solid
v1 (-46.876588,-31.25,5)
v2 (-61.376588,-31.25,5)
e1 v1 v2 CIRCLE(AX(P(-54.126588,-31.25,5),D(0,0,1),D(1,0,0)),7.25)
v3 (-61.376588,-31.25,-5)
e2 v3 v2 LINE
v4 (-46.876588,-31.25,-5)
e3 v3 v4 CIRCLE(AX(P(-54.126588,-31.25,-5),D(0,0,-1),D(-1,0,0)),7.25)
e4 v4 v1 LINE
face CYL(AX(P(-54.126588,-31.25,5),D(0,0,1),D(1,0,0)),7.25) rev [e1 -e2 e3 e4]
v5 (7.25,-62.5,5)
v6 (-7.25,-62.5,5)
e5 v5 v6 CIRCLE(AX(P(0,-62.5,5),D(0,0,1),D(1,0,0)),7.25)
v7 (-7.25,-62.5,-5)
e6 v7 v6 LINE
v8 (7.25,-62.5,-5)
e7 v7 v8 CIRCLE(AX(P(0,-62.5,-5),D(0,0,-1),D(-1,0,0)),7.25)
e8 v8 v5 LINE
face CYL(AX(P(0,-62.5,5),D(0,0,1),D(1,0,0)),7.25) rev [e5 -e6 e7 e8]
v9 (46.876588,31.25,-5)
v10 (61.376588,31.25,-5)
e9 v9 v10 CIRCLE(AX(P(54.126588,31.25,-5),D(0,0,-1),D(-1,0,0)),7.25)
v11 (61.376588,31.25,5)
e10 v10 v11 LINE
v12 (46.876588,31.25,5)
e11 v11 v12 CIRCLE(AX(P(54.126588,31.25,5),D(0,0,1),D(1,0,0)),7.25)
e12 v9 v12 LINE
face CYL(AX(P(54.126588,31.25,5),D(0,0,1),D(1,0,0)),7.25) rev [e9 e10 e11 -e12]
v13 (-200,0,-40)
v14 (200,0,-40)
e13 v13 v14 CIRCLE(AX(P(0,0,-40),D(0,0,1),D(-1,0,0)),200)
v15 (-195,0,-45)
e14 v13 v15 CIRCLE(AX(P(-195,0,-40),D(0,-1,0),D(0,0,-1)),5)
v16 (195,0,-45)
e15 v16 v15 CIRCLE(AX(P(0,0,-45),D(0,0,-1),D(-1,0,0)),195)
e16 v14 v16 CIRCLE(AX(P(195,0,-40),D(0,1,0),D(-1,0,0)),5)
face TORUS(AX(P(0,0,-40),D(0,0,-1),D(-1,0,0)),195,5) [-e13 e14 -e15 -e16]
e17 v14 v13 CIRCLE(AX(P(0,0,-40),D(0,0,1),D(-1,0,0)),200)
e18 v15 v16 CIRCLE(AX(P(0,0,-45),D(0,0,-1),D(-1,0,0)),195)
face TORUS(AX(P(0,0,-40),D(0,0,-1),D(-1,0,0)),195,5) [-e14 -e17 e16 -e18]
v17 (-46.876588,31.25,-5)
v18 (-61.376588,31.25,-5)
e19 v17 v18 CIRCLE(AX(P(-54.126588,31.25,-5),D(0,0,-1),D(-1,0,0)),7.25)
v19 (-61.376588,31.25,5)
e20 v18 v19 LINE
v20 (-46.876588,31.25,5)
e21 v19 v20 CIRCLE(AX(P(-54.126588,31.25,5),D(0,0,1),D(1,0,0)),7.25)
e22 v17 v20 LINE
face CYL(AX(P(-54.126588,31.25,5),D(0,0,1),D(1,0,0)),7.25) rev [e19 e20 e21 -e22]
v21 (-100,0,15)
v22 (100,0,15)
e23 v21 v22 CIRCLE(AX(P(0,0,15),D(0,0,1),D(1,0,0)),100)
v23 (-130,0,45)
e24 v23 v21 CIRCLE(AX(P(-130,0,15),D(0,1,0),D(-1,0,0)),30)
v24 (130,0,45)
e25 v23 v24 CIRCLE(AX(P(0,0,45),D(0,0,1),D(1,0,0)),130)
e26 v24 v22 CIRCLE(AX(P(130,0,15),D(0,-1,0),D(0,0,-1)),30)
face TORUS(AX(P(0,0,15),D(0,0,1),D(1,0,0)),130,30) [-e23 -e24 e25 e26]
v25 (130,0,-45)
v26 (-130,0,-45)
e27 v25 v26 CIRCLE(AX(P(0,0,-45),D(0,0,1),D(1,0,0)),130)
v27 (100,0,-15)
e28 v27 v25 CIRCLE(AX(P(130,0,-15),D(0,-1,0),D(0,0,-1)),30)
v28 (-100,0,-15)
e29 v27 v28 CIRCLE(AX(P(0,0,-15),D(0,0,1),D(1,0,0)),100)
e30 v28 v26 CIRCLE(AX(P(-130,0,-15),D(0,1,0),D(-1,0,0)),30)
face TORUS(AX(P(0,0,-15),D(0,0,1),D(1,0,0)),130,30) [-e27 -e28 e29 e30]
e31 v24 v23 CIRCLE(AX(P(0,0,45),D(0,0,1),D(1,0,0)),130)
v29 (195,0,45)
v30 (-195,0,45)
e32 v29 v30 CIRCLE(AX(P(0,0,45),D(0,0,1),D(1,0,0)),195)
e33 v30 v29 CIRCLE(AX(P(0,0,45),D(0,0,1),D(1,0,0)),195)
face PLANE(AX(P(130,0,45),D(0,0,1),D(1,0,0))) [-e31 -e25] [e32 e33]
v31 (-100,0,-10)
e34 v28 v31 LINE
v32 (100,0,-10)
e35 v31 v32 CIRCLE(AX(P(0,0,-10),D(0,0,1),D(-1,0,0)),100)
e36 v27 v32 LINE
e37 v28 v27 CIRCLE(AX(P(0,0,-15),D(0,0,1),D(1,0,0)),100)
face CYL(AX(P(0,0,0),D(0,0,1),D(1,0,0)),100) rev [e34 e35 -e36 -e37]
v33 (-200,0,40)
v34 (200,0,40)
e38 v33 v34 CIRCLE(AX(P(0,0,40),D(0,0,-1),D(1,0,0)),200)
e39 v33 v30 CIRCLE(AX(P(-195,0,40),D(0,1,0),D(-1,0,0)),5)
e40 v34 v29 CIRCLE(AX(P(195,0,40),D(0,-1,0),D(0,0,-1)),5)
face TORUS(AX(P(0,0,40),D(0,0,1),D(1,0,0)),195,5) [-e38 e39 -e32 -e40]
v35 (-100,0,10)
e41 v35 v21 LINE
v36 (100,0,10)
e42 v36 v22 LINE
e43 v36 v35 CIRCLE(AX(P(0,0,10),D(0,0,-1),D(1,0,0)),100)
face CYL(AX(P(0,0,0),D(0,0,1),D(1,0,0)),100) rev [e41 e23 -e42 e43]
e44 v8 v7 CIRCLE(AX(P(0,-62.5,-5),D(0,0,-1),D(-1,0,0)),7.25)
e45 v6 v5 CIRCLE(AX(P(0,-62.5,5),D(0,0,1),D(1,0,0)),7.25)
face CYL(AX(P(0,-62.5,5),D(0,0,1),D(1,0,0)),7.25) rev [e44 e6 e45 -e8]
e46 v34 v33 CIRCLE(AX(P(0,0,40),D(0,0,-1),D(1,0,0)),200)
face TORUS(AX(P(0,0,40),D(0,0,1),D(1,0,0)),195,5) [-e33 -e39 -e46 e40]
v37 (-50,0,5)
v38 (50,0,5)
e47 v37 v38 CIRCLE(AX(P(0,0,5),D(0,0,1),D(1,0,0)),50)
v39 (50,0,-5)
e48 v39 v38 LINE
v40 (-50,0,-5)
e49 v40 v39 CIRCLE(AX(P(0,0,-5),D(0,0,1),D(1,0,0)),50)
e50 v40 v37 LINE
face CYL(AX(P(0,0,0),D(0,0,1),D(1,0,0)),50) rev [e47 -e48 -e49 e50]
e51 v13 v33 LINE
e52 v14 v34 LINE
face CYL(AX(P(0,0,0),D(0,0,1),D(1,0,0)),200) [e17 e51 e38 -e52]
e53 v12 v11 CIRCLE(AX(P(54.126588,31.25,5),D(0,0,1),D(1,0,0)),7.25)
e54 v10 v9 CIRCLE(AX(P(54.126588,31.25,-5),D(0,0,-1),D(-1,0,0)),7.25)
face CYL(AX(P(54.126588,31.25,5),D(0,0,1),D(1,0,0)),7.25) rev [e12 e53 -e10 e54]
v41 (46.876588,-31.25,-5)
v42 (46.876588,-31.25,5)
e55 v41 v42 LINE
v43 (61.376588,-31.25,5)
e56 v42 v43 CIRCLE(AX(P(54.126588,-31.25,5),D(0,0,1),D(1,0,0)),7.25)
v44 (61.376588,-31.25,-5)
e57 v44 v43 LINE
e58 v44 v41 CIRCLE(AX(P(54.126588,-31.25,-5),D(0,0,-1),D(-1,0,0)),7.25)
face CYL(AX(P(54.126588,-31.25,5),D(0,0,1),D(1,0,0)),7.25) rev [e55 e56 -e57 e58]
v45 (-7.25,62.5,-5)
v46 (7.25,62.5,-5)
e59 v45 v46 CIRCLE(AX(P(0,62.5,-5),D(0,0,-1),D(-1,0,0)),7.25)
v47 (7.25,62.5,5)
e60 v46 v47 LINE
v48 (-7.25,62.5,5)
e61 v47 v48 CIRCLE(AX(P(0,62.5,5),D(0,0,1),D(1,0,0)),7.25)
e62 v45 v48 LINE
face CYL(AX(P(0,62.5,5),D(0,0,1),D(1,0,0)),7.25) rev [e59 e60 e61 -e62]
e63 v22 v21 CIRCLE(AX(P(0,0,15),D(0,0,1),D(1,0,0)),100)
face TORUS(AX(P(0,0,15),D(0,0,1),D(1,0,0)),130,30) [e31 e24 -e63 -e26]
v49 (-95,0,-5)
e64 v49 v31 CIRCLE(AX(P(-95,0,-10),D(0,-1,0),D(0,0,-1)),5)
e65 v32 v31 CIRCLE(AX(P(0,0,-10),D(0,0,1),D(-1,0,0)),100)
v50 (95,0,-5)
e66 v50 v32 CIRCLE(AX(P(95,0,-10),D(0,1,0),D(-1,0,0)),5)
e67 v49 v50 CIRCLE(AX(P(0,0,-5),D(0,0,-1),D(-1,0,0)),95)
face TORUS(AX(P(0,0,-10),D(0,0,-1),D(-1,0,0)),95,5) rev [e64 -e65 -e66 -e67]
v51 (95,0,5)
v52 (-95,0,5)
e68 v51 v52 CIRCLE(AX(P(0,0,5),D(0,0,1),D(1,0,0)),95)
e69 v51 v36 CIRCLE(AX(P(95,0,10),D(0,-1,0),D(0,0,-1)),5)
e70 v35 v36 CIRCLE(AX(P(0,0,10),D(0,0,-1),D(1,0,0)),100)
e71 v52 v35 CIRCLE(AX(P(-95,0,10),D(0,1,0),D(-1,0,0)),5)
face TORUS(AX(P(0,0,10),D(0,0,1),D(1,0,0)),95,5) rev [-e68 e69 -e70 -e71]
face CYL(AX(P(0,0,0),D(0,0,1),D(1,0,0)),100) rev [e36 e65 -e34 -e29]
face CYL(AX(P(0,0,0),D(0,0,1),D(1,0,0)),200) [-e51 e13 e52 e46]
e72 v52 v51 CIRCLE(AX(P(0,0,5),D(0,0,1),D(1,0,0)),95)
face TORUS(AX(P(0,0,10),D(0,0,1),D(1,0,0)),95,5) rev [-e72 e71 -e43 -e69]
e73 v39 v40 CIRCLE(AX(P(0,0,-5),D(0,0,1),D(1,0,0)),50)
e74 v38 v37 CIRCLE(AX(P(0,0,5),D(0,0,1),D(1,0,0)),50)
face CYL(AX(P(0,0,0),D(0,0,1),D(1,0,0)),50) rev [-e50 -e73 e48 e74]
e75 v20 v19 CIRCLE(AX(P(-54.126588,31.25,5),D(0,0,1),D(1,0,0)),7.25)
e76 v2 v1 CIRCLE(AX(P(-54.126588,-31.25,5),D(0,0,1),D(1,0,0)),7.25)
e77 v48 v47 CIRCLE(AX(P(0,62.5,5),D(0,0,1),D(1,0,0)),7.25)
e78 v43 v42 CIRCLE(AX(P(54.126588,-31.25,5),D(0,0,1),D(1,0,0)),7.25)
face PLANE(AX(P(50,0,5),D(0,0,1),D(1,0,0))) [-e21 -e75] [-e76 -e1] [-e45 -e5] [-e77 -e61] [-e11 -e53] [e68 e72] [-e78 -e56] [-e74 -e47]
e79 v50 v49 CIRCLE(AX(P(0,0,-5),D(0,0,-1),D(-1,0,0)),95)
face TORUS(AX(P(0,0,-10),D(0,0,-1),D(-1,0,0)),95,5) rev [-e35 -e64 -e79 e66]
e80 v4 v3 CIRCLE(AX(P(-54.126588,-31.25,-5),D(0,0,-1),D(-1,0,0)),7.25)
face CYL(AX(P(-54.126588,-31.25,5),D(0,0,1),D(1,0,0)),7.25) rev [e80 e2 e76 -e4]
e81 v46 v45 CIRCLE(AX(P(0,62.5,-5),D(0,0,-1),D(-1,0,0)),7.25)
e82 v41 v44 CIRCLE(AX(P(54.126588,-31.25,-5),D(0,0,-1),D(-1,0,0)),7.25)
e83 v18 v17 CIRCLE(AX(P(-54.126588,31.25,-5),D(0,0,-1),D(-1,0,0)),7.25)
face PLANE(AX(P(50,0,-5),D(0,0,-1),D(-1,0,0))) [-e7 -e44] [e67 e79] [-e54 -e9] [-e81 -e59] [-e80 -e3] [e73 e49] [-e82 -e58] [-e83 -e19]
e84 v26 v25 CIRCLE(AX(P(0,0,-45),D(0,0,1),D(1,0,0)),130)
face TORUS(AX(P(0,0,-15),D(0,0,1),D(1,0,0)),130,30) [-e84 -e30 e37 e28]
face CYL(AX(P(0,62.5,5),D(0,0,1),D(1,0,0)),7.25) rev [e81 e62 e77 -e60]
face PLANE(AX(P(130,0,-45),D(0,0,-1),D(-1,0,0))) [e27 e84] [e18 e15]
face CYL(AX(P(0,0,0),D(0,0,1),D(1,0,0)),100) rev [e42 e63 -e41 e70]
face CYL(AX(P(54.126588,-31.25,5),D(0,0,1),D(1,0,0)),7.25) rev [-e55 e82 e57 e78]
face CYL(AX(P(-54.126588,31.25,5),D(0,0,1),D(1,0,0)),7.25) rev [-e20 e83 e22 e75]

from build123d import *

# Parameters (mm, degrees)
FILLET1_R                    = 5
F_14_5_14_5_DIAMETER_HOLE1_D = 14.5


with BuildPart() as part:
    # Sketch2 → Revolve1 (revolve)
    with BuildSketch(Plane(origin=(0, 0, 0), x_dir=(1, 0, 0), z_dir=(0, 1, 0))):
        with BuildLine():
            Line((50, -5), (50, 5))
            Line((50, 5), (100, 5))
            Line((100, 5), (100, 15))
            ThreePointArc((100, 15), (108.786796564, 36.213203436), (130, 45))
            Line((130, 45), (200, 45))
            Line((200, 45), (200, -45))
            Line((200, -45), (130, -45))
            ThreePointArc((130, -45), (108.786796564, -36.213203436), (100, -15))
            Line((100, -15), (100, -5))
            Line((100, -5), (50, -5))
        make_face()
    revolve(axis=Axis((0, 0, 0), (0, 0, -1)))

    # Fillet1
    fillet1_edges = [part.edges().sort_by_distance(p)[0] for p in [
        (-100, 0, -5),
        (-100, 0, 5),
        (-200, 0, 45),
        (-200, 0, -45),
    ]]
    fillet(fillet1_edges, radius=FILLET1_R)

    # Ø14.5 (14.5) Diameter Hole1 (through all)
    with Locations(Plane.XY.offset(5)):
        with Locations((0, 62.5), (54.126587737, 31.25), (54.126587737, -31.25), (0, -62.5), (-54.126587737, -31.25), (-54.126587737, 31.25)):
            Hole(F_14_5_14_5_DIAMETER_HOLE1_D / 2)


solid = part.part
